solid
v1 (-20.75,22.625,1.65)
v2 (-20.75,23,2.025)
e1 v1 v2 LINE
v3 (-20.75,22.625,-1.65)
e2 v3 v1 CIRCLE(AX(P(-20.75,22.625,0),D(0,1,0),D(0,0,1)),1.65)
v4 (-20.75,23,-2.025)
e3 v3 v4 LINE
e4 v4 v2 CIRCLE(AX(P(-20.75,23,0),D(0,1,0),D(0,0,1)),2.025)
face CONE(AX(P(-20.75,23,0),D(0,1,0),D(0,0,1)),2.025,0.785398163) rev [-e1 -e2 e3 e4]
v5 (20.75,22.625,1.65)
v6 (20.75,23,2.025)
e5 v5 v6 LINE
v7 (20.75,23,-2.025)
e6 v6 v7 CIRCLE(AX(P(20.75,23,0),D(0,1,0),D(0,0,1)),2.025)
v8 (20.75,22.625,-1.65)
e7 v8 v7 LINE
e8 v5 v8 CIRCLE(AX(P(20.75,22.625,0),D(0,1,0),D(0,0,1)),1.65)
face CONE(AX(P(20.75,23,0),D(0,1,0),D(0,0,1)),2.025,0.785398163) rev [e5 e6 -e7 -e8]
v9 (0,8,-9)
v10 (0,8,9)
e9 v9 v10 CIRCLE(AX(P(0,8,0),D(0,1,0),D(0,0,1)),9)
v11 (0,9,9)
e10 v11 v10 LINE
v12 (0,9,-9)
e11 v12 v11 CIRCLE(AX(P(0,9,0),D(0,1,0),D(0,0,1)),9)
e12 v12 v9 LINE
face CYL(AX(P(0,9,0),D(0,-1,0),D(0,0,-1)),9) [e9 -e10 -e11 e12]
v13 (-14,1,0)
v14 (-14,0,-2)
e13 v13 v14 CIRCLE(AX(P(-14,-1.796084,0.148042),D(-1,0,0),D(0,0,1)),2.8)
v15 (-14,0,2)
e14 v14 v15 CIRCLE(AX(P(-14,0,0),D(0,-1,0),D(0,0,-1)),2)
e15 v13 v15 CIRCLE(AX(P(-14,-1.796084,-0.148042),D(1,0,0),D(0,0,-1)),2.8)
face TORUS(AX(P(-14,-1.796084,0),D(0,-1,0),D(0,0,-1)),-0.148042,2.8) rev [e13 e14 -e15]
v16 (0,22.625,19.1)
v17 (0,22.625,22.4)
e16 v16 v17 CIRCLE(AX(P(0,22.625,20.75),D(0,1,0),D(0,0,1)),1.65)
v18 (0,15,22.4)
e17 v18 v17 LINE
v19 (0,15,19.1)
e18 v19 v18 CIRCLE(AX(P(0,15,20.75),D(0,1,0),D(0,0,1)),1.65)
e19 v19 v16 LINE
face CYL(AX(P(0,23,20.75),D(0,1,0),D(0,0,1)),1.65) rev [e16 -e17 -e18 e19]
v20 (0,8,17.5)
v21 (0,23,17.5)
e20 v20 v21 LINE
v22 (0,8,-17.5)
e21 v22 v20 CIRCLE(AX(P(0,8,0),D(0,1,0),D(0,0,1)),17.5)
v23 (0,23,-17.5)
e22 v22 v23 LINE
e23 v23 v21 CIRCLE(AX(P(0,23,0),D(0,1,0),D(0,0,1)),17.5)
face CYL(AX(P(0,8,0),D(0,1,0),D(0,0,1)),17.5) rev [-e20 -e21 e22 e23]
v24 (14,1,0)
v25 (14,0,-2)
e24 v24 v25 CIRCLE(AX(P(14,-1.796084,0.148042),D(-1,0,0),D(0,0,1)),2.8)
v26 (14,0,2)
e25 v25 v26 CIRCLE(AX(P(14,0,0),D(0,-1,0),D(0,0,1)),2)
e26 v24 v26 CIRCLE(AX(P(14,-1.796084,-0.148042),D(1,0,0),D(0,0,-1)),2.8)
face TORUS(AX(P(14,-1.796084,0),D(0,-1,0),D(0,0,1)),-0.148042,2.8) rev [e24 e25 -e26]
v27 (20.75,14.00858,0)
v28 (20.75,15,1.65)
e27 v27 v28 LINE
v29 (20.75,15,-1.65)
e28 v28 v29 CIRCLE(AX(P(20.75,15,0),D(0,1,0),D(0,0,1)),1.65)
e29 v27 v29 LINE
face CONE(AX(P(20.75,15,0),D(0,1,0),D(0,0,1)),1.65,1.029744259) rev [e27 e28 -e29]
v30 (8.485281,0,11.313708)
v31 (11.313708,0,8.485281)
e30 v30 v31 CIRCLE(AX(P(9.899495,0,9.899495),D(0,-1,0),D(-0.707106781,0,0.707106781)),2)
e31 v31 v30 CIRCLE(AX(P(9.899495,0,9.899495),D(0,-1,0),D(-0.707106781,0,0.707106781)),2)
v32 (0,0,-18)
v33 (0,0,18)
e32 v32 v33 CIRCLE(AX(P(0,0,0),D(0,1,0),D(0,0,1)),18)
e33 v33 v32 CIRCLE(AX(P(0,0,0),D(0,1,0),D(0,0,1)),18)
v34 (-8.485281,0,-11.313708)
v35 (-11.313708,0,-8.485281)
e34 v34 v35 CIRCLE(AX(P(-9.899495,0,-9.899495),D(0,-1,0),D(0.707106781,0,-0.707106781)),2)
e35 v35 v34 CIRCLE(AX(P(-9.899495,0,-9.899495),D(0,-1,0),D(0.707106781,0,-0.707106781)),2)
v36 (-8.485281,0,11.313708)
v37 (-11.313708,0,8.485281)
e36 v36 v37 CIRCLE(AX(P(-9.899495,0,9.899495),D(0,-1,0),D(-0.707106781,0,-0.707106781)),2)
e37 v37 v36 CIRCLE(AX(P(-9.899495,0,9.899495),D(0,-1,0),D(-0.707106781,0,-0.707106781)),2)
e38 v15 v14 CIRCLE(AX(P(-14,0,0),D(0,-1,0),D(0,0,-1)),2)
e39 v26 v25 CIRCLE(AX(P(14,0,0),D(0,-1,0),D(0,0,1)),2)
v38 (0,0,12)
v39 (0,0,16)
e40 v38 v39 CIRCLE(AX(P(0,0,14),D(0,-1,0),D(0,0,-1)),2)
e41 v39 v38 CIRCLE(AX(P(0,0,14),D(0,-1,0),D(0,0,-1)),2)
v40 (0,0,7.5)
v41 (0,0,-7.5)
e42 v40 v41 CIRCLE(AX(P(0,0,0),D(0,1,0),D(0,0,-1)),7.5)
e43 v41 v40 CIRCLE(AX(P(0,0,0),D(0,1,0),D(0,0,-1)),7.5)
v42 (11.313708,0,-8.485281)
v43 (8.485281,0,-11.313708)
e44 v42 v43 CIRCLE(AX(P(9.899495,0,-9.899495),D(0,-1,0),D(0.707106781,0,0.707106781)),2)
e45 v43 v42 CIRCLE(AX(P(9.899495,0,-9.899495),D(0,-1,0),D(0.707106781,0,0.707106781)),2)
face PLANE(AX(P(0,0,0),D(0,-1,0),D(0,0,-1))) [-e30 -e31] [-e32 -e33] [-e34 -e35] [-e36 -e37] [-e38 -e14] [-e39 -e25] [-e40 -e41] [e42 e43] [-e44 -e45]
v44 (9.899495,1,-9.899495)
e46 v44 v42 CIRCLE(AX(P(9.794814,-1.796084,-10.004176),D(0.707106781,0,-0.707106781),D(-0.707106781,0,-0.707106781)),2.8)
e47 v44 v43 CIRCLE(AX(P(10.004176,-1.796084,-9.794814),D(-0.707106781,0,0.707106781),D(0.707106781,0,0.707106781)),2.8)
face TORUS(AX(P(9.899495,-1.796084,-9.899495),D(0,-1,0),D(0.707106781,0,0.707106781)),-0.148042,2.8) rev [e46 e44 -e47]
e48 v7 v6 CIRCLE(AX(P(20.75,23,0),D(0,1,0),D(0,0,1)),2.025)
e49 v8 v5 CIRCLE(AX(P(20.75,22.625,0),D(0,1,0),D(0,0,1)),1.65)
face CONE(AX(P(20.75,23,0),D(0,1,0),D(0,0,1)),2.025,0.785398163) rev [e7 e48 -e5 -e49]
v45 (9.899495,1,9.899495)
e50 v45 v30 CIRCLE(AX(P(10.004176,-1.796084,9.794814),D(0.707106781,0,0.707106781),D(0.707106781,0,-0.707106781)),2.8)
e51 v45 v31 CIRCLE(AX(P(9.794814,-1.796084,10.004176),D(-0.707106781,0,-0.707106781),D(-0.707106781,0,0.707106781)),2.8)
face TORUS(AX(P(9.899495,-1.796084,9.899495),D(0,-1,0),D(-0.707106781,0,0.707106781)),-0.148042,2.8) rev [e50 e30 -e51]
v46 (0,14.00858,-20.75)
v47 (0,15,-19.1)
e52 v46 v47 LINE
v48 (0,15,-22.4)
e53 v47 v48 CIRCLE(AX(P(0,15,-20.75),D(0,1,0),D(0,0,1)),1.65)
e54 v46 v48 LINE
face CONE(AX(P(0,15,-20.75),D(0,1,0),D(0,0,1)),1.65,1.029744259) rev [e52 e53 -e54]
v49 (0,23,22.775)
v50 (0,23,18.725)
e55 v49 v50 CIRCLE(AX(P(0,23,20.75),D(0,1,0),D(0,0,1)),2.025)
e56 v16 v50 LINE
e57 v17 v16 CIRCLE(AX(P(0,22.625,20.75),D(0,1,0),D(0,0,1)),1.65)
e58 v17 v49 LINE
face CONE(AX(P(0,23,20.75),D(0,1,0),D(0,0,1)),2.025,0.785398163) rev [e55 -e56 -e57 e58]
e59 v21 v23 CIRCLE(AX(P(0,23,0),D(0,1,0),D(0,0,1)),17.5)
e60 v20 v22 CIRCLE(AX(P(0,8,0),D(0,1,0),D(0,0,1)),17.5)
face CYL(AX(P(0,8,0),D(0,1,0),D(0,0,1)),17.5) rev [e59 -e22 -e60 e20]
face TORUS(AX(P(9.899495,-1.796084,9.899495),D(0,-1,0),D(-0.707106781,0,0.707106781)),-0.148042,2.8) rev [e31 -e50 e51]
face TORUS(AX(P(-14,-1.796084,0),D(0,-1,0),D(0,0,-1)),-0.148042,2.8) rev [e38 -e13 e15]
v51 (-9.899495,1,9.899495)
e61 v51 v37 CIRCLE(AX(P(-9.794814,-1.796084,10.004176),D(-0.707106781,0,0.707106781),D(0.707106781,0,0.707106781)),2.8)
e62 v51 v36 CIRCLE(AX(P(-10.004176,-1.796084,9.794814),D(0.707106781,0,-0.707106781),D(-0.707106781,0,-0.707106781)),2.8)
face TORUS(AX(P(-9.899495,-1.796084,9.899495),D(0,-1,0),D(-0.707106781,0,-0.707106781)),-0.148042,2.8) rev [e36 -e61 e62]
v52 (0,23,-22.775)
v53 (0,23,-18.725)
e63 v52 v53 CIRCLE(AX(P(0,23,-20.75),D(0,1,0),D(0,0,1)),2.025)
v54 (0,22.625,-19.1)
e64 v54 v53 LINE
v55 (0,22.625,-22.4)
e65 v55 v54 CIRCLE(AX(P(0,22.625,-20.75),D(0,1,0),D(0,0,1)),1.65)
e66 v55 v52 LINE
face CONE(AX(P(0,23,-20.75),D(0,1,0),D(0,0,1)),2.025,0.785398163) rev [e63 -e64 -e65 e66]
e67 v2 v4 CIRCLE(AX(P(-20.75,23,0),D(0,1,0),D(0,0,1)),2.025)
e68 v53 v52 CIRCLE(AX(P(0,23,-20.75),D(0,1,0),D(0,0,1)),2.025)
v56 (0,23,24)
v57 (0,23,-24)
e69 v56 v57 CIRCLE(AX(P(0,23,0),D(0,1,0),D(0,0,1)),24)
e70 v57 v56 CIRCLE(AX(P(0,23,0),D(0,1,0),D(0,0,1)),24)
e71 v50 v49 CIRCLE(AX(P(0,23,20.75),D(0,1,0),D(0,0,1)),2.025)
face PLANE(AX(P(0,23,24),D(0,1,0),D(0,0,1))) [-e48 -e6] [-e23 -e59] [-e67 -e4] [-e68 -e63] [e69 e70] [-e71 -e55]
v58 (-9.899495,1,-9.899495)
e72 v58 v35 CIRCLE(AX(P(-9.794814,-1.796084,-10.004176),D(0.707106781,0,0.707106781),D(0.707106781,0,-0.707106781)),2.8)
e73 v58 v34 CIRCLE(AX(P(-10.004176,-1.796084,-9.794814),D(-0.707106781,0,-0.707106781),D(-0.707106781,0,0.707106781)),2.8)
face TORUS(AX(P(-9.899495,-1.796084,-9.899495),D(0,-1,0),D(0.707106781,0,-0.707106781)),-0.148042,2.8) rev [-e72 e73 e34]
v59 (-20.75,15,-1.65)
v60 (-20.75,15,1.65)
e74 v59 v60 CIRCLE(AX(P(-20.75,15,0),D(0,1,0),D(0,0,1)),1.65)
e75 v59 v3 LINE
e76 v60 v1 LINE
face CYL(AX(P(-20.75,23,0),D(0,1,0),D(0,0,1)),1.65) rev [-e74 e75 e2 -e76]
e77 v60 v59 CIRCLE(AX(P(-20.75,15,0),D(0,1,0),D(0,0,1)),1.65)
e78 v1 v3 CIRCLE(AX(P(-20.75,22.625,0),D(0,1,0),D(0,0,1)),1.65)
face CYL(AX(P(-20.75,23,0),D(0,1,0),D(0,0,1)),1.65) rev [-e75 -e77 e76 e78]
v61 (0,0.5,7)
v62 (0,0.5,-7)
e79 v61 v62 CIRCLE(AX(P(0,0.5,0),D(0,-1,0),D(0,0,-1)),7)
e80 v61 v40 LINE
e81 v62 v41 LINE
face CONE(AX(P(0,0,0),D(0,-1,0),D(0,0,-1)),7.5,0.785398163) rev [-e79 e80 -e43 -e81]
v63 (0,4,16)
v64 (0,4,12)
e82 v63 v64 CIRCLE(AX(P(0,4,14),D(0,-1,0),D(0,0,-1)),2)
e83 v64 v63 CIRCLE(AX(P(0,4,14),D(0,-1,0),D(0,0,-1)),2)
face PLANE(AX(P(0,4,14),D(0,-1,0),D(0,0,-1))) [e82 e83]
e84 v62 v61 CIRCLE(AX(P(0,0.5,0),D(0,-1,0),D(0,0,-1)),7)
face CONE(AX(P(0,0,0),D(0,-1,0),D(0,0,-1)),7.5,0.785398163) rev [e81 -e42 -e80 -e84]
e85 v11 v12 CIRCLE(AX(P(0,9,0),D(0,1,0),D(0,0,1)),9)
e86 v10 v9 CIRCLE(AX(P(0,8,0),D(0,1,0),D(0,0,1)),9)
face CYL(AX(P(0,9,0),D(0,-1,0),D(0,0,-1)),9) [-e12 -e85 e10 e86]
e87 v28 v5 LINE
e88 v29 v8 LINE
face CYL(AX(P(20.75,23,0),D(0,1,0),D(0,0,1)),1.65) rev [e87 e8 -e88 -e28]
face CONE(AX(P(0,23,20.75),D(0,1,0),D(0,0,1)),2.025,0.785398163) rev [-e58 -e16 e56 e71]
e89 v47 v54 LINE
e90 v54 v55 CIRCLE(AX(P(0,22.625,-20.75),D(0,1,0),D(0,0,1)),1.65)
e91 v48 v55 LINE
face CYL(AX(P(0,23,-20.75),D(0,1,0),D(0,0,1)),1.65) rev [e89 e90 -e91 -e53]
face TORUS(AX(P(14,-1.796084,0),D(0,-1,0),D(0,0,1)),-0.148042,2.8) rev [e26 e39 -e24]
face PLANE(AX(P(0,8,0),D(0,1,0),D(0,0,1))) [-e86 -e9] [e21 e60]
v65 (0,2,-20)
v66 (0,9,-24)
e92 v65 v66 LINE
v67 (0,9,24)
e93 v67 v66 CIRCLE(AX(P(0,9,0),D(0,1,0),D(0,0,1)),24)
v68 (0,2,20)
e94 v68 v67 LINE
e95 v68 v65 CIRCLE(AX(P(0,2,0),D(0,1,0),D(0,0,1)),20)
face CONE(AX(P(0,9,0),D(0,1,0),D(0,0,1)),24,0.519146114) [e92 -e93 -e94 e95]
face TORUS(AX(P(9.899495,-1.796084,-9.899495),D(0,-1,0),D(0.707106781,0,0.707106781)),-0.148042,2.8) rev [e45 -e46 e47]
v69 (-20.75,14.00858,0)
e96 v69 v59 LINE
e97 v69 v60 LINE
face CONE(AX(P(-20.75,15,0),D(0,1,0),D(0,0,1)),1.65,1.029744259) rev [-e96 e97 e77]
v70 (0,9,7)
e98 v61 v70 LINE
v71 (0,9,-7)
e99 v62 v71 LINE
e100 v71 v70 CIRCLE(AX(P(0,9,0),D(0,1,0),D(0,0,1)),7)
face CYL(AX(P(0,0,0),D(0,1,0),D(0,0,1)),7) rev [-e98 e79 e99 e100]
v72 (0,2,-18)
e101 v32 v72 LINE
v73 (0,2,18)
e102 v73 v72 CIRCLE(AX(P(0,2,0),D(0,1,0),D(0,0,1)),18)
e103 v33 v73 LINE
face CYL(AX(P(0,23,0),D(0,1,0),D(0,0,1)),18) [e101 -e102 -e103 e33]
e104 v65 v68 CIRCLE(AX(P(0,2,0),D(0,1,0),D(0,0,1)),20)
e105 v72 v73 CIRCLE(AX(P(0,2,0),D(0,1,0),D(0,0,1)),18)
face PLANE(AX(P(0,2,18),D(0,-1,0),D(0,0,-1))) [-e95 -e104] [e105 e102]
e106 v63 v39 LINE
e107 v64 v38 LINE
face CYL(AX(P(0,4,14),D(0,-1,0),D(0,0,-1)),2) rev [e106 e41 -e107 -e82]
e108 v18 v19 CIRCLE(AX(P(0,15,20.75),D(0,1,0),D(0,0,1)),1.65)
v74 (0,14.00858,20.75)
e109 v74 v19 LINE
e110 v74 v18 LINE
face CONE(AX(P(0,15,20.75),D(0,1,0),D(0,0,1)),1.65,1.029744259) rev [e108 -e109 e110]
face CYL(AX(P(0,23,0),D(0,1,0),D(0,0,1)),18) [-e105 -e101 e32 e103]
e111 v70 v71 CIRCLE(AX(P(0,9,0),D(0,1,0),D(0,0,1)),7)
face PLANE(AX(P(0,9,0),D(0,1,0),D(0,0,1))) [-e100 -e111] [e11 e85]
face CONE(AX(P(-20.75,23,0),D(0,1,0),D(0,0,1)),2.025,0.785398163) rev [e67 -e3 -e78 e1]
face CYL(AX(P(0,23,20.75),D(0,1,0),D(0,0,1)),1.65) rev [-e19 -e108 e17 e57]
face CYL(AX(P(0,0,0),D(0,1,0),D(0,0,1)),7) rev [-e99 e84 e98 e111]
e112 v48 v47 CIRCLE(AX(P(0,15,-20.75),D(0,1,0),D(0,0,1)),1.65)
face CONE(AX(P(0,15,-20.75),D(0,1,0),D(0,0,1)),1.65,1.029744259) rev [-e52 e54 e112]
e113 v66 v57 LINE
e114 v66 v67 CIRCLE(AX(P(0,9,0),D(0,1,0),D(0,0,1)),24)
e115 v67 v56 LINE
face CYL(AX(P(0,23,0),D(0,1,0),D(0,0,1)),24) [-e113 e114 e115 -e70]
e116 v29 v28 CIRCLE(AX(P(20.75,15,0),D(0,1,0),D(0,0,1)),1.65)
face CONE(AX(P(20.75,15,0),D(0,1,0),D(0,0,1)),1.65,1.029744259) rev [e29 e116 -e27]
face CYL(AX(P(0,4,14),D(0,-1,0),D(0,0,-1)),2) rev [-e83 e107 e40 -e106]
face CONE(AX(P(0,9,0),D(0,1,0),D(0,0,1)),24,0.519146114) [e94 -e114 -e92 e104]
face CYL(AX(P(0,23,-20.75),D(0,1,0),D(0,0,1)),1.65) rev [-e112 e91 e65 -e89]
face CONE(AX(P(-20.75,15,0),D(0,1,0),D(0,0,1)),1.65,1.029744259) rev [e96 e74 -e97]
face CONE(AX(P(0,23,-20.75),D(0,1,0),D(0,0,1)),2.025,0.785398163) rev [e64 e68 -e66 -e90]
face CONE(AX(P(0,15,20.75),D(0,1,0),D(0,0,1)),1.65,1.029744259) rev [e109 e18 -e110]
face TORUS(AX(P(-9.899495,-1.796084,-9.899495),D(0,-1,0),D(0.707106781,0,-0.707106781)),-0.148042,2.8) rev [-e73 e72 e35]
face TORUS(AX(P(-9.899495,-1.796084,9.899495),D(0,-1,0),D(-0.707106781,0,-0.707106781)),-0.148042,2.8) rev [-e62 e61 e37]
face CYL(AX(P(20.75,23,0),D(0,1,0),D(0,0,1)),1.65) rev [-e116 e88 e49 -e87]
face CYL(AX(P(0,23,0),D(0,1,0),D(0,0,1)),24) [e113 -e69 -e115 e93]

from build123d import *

# Parameters (mm, degrees)
SKETCH2_R           = 17.5
CUT_EXTRUDE1_DEPTH  = 15
SKETCH3_R           = 9
BOSS_EXTRUDE1_DEPTH = 1
SKETCH4_R           = 7
CUT_EXTRUDE2_DEPTH  = 37.715119501
SKETCH5_R           = 2
CUT_EXTRUDE3_DEPTH  = 4
CIRPATTERN1_COUNT   = 8
CIRPATTERN2_COUNT   = 4
CHAMFER1_SIZE       = 0.5


with BuildPart() as part:
    # Sketch1 → Revolve1 (revolve)
    with BuildSketch(Plane(origin=(0, 0, 0), x_dir=(0, 0, -1), z_dir=(1, 0, 0))):
        Polygon((0, 0), (-18, 0), (-18, 2), (-20, 2), (-24, 9), (-24, 23), (0, 23), align=None)
    revolve(axis=Axis((0, 23, 0), (0, -1, 0)))

    # Sketch2 → Cut-Extrude1 (cut)
    with BuildSketch(Plane(origin=(0, 23, 0), x_dir=(1, 0, 0), z_dir=(0, 1, 0))):
        with Locations(Location((0, 0, 0), (0, 0, 270))):
            Circle(SKETCH2_R)
    extrude(amount=-CUT_EXTRUDE1_DEPTH, mode=Mode.SUBTRACT)

    # Sketch3 → Boss-Extrude1 (add)
    with BuildSketch(Plane(origin=(0, 8, 0), x_dir=(1, 0, 0), z_dir=(0, 1, 0))):
        with Locations(Location((0, 0, 0), (0, 0, 270))):
            Circle(SKETCH3_R)
    extrude(amount=BOSS_EXTRUDE1_DEPTH)

    # Sketch4 → Cut-Extrude2 (cut, through all)
    with BuildSketch(Plane(origin=(0, 9, 0), x_dir=(1, 0, 0), z_dir=(0, 1, 0))):
        with Locations(Location((0, 0, 0), (0, 0, 270))):
            Circle(SKETCH4_R)
    extrude(amount=-CUT_EXTRUDE2_DEPTH, mode=Mode.SUBTRACT)

    # Sketch5 → Cut-Extrude3 (cut)
    with BuildSketch(Plane.XZ):
        with Locations(Location((0, 14, 0), (0, 0, 270))):
            Circle(SKETCH5_R)
    extrude(amount=-CUT_EXTRUDE3_DEPTH, mode=Mode.SUBTRACT)

    # Sketch6 → Cut-Revolve1 (revolve, cut)
    with BuildSketch(Plane.XY):
        with BuildLine():
            Line((-16, 0), (-14, 0))
            Line((-14, 0), (-14, 1))
            ThreePointArc((-14, 1), (-15.104156256, 0.708312513), (-16, 0))
        make_face()
    cut_revolve1 = revolve(axis=Axis((-14, 0, 0), (0, 1, 0)), mode=Mode.SUBTRACT)

    # CirPattern1: Cut-Revolve1 ×8 about axis, 2 skipped
    cirpattern1_axis = Axis((0, 0, 0), (0, 1, 0))
    add([cut_revolve1.rotate(cirpattern1_axis, i * 360 / CIRPATTERN1_COUNT) for i in range(1, CIRPATTERN1_COUNT) if i not in (2, 6)], mode=Mode.SUBTRACT)

    # Sketch8 → M4 Tapped Hole1 (revolve, cut)
    with BuildSketch(Plane(origin=(0, 23, -20.75), x_dir=(0, 0, 1), z_dir=(1, 0, 0))):
        Polygon((0, 0), (0, 8.991420021), (1.65, 8), (1.65, 0.375), (2.025, 0), align=None)
    m4_tapped_hole1 = revolve(axis=Axis((0, 29.35, -20.75), (0, -1, 0)), mode=Mode.SUBTRACT)

    # CirPattern2: M4 Tapped Hole1 ×4 about axis
    cirpattern2_axis = Axis((0, 0, 0), (0, 1, 0))
    for i in range(1, CIRPATTERN2_COUNT):
        add(m4_tapped_hole1.rotate(cirpattern2_axis, i * 360 / CIRPATTERN2_COUNT), mode=Mode.SUBTRACT)

    # Chamfer1
    chamfer1_edges = [part.edges().sort_by_distance(p)[0] for p in [
        (0, 0, -7),
    ]]
    chamfer(chamfer1_edges, length=CHAMFER1_SIZE)


solid = part.part
